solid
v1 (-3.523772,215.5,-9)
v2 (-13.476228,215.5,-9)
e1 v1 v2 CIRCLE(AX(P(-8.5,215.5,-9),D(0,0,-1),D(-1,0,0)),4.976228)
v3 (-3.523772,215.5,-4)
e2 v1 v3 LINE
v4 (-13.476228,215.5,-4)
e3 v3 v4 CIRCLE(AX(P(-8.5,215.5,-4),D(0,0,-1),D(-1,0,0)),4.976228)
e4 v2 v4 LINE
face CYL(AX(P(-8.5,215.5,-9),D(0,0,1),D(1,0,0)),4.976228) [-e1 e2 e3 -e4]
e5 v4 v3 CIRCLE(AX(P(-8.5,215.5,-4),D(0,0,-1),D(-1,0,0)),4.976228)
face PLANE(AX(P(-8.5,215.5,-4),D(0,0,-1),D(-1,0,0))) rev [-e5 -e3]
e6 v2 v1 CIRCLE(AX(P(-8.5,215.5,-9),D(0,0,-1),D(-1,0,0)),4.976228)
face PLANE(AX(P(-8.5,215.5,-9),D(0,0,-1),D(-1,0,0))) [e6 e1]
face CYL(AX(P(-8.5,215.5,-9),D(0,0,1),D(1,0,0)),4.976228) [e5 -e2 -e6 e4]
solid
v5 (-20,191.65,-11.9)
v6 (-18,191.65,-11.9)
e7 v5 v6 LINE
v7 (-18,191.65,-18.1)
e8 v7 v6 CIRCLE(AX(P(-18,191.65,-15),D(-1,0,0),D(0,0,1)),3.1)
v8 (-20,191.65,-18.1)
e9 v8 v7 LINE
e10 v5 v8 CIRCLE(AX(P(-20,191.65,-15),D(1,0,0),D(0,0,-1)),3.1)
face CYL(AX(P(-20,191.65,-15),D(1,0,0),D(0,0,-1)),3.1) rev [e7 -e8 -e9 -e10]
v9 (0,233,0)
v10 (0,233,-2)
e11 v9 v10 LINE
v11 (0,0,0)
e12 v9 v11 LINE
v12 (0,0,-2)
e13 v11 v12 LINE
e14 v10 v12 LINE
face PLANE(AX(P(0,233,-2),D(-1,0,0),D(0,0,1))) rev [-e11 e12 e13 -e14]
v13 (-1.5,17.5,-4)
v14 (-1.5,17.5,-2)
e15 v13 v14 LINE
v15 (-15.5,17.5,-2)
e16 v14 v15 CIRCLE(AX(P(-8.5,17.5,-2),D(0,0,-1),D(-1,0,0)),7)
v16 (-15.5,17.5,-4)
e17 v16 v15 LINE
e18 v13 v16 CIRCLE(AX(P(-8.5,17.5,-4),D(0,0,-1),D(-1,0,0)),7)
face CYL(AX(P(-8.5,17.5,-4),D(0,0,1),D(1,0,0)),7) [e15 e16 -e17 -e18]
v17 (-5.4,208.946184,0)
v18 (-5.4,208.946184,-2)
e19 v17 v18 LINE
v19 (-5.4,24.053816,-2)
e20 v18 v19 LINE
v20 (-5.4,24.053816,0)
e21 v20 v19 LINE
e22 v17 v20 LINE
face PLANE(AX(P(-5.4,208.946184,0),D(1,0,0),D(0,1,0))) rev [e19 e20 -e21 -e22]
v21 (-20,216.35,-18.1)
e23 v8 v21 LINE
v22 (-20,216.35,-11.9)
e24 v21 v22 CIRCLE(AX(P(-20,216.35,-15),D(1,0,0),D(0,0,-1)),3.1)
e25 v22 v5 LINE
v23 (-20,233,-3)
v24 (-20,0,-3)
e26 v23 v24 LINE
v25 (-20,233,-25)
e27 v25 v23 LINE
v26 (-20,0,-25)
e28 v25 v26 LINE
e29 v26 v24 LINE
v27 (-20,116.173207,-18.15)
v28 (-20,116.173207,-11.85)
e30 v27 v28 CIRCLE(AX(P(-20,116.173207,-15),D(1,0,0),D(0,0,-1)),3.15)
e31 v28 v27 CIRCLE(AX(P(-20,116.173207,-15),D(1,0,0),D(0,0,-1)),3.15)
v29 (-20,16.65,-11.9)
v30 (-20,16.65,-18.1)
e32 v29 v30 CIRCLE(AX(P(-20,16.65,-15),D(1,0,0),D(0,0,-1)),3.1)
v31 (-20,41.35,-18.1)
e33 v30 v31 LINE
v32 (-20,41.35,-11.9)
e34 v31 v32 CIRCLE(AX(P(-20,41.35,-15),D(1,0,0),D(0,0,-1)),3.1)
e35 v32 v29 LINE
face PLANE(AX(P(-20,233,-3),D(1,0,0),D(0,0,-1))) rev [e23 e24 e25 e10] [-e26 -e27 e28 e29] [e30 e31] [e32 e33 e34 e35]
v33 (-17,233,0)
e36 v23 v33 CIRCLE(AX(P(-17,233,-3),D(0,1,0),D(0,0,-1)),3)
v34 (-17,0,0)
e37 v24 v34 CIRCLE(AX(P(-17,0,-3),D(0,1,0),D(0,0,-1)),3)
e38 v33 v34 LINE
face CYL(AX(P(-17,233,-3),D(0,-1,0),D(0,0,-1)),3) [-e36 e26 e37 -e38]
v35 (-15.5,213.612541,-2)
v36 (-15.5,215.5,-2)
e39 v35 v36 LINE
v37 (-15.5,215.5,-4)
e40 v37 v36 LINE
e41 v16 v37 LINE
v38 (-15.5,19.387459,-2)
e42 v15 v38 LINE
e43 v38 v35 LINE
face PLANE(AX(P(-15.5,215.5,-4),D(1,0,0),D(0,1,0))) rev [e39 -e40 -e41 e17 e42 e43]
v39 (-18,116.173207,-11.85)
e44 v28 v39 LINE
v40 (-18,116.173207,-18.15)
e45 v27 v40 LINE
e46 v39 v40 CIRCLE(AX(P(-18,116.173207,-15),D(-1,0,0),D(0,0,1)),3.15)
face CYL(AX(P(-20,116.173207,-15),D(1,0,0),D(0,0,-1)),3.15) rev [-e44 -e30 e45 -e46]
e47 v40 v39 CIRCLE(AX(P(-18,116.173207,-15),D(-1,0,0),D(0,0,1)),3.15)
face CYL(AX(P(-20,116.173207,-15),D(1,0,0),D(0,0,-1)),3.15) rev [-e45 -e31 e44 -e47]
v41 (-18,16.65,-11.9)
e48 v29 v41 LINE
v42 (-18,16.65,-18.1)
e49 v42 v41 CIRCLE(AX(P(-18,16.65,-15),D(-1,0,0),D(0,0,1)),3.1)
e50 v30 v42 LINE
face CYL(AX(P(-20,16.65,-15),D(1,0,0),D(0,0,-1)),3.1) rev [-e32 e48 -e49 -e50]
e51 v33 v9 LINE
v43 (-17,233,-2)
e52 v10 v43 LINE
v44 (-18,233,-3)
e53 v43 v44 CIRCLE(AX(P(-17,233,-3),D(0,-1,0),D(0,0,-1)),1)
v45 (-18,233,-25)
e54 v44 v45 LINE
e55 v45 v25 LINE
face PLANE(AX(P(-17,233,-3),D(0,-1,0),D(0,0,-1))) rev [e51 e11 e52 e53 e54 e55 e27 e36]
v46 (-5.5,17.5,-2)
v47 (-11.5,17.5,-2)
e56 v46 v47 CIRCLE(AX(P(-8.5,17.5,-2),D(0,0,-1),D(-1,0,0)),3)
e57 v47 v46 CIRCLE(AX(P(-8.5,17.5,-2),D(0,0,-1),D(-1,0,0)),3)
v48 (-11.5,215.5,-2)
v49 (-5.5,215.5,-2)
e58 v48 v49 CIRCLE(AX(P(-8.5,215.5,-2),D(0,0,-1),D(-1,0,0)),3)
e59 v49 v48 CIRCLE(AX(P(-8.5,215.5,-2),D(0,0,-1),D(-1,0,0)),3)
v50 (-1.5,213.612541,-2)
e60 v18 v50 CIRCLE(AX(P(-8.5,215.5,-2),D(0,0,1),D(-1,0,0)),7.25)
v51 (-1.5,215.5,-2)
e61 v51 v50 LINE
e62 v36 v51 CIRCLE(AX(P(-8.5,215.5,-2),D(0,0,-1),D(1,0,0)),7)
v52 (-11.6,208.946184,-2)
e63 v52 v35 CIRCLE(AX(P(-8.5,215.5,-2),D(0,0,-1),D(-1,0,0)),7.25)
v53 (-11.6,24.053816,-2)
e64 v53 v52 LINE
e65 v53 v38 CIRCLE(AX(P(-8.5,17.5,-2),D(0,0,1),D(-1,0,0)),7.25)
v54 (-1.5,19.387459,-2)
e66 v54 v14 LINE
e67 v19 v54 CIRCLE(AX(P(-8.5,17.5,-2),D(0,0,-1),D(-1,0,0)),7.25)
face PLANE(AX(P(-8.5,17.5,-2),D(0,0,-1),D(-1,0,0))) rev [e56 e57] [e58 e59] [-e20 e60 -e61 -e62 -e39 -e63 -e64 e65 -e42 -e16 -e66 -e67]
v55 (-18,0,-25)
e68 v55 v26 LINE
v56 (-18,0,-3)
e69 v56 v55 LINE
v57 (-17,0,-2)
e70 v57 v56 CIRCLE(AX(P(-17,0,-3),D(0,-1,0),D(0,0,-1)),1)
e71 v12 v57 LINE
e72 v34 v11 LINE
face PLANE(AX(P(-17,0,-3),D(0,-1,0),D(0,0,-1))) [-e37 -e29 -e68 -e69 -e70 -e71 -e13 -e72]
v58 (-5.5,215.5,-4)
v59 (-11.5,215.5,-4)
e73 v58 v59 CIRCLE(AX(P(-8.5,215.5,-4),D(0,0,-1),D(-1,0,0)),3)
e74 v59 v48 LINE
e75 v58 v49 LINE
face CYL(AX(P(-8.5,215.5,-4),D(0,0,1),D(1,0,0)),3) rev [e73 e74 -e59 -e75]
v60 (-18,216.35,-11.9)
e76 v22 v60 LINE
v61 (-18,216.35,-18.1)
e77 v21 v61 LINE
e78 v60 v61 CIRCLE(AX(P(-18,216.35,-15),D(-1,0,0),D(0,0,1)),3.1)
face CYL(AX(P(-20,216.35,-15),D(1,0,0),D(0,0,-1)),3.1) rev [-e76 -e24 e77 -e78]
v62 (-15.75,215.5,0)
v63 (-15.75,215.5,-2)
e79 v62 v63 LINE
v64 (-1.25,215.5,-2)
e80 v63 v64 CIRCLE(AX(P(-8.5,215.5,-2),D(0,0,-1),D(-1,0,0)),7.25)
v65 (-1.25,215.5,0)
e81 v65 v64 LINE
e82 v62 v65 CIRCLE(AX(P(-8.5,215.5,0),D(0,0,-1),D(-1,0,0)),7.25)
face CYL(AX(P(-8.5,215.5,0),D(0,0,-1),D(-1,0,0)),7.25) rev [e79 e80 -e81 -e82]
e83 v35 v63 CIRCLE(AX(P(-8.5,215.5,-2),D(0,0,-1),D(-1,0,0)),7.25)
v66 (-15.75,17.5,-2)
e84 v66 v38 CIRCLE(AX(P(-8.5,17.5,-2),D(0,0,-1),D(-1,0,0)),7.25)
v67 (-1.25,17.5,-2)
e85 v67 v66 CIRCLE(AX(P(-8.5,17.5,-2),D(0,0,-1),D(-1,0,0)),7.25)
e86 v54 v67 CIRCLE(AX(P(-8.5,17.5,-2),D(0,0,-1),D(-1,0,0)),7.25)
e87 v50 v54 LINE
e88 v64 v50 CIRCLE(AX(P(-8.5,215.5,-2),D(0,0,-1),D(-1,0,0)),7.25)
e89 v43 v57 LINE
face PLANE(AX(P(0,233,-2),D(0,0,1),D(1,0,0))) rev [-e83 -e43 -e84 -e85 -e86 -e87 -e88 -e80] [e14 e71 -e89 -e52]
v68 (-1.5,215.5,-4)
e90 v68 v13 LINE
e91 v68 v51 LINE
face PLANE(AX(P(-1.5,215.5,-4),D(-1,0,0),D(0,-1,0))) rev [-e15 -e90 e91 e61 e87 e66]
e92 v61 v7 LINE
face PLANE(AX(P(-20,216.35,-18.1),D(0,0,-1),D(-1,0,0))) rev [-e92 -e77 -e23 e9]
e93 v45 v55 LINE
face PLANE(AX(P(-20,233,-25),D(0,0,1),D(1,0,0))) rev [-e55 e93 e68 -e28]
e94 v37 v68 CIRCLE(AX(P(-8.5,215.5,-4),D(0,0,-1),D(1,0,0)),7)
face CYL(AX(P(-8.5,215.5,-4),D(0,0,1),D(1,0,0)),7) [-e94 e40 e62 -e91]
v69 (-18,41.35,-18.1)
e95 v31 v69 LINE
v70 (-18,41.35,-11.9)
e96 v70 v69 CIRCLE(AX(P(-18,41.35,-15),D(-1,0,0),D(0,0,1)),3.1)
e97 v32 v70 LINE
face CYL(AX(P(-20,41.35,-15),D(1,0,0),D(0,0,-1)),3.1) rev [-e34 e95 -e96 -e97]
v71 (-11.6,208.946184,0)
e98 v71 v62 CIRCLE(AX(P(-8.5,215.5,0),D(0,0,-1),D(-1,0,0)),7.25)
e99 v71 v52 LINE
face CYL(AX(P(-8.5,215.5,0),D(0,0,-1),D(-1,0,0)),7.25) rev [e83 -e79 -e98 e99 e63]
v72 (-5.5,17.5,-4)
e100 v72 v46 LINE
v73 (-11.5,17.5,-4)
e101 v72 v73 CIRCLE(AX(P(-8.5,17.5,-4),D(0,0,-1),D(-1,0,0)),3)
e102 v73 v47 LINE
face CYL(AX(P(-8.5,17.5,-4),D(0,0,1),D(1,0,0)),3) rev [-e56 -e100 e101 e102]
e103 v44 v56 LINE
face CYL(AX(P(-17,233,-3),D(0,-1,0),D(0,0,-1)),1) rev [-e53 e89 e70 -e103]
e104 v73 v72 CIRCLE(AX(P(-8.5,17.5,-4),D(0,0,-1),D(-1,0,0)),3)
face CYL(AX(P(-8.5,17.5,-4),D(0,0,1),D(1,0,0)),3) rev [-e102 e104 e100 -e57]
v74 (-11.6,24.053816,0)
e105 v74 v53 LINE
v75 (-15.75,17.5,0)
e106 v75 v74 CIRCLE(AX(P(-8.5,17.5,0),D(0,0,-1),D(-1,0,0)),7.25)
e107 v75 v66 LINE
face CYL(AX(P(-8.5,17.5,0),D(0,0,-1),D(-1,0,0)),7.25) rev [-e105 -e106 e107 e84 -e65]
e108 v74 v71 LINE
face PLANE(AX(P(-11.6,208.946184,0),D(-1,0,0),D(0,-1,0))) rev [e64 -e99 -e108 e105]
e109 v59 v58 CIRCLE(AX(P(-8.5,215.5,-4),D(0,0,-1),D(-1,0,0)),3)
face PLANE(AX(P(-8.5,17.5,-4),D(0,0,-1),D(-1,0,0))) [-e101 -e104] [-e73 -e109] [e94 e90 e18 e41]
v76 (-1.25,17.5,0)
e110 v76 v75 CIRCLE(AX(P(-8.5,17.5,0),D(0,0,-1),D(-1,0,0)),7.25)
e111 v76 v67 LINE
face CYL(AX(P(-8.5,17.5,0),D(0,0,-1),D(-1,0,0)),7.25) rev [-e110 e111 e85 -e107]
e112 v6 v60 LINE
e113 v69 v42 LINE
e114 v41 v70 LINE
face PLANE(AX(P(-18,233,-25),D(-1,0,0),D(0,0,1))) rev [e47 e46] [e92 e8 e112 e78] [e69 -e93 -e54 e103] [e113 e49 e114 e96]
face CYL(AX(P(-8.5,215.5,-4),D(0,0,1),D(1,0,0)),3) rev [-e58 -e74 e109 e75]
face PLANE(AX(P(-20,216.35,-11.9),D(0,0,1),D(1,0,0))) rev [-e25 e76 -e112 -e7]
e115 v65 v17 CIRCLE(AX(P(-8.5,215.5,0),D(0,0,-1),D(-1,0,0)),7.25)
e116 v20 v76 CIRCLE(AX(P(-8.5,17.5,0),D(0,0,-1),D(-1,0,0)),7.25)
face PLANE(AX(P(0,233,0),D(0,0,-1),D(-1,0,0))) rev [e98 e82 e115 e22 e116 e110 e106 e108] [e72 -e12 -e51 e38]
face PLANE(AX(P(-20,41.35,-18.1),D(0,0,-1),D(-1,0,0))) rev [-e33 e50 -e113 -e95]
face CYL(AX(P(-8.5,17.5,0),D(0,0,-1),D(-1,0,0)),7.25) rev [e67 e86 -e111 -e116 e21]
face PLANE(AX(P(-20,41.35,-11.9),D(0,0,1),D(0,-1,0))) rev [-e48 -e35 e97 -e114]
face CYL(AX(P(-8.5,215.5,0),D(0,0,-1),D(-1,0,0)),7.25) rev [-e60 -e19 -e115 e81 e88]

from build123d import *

# Parameters (mm, degrees)
BOSS_EXTRUDE1_DEPTH = 233
SKETCH2_R           = 3.15
CUT_EXTRUDE1_DEPTH  = 235.882949573
CUT_EXTRUDE2_DEPTH  = 235.985105911
SKETCH4_R           = 3
BOSS_EXTRUDE2_DEPTH = 2
SKETCH5_R           = 4.976227588
BOSS_EXTRUDE3_DEPTH = 5


with BuildPart() as part:
    # Sketch1 → Boss-Extrude1 (new body)
    with BuildSketch(Plane(origin=(0, 0, 0), x_dir=(1, 0, 0), z_dir=(0, 1, 0))):
        with BuildLine():
            Line((0, 0), (-17, 0))
            ThreePointArc((-17, 0), (-19.121320344, 0.878679656), (-20, 3))
            Line((-20, 3), (-20, 8.423888846))
            Line((-20, 8.423888846), (-20, 25))
            Line((-20, 25), (-18, 25))
            Line((-18, 25), (-18, 8.423888846))
            Line((-18, 8.423888846), (-18, 3))
            ThreePointArc((-18, 3), (-17.707106781, 2.292893219), (-17, 2))
            Line((-17, 2), (0, 2))
            Line((0, 2), (0, 0))
        make_face()
    extrude(amount=BOSS_EXTRUDE1_DEPTH)

    # Sketch2 → Cut-Extrude1 (cut, through all)
    with BuildSketch(Plane(origin=(-16, 0, 0), x_dir=(0, 0, -1), z_dir=(1, 0, 0))):
        with Locations((15, 116.173206962)):
            Circle(SKETCH2_R)
        with BuildLine():
            Line((18.1, 216.35), (18.1, 191.65))
            ThreePointArc((18.1, 191.65), (15, 188.55), (11.9, 191.65))
            Line((11.9, 191.65), (11.9, 216.35))
            ThreePointArc((11.9, 216.35), (15, 219.45), (18.1, 216.35))
        make_face()
        with BuildLine():
            Line((18.1, 41.35), (18.1, 16.65))
            ThreePointArc((18.1, 16.65), (15, 13.55), (11.9, 16.65))
            Line((11.9, 16.65), (11.9, 41.35))
            ThreePointArc((11.9, 41.35), (15, 44.45), (18.1, 41.35))
        make_face()
    extrude(amount=-CUT_EXTRUDE1_DEPTH, mode=Mode.SUBTRACT)

    # Sketch3 → Cut-Extrude2 (cut, through all)
    with BuildSketch(Plane(origin=(0, 0, -2), x_dir=(-1, 0, 0), z_dir=(0, 0, -1))):
        with BuildLine():
            Line((5.4, 208.946184318), (5.4, 24.053815682))
            ThreePointArc((5.4, 24.053815682), (8.5, 10.25), (11.6, 24.053815682))
            Line((11.6, 24.053815682), (11.6, 208.946184318))
            ThreePointArc((11.6, 208.946184318), (8.5, 222.75), (5.4, 208.946184318))
        make_face()
    extrude(amount=-CUT_EXTRUDE2_DEPTH, mode=Mode.SUBTRACT)

    # Sketch4 → Boss-Extrude2 (add)
    with BuildSketch(Plane(origin=(0, 0, -2), x_dir=(-1, 0, 0), z_dir=(0, 0, -1))):
        with BuildLine():
            Line((1.5, 215.5), (1.5, 17.5))
            ThreePointArc((1.5, 17.5), (8.5, 10.5), (15.5, 17.5))
            Line((15.5, 17.5), (15.5, 215.5))
            ThreePointArc((15.5, 215.5), (8.5, 222.5), (1.5, 215.5))
        make_face()
        with Locations((8.5, 215.5)):
            Circle(SKETCH4_R, mode=Mode.SUBTRACT)
        with Locations((8.5, 17.5)):
            Circle(SKETCH4_R, mode=Mode.SUBTRACT)
    extrude(amount=BOSS_EXTRUDE2_DEPTH)


with BuildPart() as body_2:
    # Sketch5 → Boss-Extrude3 (new body)
    with BuildSketch(Plane(origin=(0, 0, -4), x_dir=(-1, 0, 0), z_dir=(0, 0, -1))):
        with Locations((8.5, 215.5)):
            Circle(SKETCH5_R)
    extrude(amount=BOSS_EXTRUDE3_DEPTH)


solid = Compound([part.part, body_2.part])
